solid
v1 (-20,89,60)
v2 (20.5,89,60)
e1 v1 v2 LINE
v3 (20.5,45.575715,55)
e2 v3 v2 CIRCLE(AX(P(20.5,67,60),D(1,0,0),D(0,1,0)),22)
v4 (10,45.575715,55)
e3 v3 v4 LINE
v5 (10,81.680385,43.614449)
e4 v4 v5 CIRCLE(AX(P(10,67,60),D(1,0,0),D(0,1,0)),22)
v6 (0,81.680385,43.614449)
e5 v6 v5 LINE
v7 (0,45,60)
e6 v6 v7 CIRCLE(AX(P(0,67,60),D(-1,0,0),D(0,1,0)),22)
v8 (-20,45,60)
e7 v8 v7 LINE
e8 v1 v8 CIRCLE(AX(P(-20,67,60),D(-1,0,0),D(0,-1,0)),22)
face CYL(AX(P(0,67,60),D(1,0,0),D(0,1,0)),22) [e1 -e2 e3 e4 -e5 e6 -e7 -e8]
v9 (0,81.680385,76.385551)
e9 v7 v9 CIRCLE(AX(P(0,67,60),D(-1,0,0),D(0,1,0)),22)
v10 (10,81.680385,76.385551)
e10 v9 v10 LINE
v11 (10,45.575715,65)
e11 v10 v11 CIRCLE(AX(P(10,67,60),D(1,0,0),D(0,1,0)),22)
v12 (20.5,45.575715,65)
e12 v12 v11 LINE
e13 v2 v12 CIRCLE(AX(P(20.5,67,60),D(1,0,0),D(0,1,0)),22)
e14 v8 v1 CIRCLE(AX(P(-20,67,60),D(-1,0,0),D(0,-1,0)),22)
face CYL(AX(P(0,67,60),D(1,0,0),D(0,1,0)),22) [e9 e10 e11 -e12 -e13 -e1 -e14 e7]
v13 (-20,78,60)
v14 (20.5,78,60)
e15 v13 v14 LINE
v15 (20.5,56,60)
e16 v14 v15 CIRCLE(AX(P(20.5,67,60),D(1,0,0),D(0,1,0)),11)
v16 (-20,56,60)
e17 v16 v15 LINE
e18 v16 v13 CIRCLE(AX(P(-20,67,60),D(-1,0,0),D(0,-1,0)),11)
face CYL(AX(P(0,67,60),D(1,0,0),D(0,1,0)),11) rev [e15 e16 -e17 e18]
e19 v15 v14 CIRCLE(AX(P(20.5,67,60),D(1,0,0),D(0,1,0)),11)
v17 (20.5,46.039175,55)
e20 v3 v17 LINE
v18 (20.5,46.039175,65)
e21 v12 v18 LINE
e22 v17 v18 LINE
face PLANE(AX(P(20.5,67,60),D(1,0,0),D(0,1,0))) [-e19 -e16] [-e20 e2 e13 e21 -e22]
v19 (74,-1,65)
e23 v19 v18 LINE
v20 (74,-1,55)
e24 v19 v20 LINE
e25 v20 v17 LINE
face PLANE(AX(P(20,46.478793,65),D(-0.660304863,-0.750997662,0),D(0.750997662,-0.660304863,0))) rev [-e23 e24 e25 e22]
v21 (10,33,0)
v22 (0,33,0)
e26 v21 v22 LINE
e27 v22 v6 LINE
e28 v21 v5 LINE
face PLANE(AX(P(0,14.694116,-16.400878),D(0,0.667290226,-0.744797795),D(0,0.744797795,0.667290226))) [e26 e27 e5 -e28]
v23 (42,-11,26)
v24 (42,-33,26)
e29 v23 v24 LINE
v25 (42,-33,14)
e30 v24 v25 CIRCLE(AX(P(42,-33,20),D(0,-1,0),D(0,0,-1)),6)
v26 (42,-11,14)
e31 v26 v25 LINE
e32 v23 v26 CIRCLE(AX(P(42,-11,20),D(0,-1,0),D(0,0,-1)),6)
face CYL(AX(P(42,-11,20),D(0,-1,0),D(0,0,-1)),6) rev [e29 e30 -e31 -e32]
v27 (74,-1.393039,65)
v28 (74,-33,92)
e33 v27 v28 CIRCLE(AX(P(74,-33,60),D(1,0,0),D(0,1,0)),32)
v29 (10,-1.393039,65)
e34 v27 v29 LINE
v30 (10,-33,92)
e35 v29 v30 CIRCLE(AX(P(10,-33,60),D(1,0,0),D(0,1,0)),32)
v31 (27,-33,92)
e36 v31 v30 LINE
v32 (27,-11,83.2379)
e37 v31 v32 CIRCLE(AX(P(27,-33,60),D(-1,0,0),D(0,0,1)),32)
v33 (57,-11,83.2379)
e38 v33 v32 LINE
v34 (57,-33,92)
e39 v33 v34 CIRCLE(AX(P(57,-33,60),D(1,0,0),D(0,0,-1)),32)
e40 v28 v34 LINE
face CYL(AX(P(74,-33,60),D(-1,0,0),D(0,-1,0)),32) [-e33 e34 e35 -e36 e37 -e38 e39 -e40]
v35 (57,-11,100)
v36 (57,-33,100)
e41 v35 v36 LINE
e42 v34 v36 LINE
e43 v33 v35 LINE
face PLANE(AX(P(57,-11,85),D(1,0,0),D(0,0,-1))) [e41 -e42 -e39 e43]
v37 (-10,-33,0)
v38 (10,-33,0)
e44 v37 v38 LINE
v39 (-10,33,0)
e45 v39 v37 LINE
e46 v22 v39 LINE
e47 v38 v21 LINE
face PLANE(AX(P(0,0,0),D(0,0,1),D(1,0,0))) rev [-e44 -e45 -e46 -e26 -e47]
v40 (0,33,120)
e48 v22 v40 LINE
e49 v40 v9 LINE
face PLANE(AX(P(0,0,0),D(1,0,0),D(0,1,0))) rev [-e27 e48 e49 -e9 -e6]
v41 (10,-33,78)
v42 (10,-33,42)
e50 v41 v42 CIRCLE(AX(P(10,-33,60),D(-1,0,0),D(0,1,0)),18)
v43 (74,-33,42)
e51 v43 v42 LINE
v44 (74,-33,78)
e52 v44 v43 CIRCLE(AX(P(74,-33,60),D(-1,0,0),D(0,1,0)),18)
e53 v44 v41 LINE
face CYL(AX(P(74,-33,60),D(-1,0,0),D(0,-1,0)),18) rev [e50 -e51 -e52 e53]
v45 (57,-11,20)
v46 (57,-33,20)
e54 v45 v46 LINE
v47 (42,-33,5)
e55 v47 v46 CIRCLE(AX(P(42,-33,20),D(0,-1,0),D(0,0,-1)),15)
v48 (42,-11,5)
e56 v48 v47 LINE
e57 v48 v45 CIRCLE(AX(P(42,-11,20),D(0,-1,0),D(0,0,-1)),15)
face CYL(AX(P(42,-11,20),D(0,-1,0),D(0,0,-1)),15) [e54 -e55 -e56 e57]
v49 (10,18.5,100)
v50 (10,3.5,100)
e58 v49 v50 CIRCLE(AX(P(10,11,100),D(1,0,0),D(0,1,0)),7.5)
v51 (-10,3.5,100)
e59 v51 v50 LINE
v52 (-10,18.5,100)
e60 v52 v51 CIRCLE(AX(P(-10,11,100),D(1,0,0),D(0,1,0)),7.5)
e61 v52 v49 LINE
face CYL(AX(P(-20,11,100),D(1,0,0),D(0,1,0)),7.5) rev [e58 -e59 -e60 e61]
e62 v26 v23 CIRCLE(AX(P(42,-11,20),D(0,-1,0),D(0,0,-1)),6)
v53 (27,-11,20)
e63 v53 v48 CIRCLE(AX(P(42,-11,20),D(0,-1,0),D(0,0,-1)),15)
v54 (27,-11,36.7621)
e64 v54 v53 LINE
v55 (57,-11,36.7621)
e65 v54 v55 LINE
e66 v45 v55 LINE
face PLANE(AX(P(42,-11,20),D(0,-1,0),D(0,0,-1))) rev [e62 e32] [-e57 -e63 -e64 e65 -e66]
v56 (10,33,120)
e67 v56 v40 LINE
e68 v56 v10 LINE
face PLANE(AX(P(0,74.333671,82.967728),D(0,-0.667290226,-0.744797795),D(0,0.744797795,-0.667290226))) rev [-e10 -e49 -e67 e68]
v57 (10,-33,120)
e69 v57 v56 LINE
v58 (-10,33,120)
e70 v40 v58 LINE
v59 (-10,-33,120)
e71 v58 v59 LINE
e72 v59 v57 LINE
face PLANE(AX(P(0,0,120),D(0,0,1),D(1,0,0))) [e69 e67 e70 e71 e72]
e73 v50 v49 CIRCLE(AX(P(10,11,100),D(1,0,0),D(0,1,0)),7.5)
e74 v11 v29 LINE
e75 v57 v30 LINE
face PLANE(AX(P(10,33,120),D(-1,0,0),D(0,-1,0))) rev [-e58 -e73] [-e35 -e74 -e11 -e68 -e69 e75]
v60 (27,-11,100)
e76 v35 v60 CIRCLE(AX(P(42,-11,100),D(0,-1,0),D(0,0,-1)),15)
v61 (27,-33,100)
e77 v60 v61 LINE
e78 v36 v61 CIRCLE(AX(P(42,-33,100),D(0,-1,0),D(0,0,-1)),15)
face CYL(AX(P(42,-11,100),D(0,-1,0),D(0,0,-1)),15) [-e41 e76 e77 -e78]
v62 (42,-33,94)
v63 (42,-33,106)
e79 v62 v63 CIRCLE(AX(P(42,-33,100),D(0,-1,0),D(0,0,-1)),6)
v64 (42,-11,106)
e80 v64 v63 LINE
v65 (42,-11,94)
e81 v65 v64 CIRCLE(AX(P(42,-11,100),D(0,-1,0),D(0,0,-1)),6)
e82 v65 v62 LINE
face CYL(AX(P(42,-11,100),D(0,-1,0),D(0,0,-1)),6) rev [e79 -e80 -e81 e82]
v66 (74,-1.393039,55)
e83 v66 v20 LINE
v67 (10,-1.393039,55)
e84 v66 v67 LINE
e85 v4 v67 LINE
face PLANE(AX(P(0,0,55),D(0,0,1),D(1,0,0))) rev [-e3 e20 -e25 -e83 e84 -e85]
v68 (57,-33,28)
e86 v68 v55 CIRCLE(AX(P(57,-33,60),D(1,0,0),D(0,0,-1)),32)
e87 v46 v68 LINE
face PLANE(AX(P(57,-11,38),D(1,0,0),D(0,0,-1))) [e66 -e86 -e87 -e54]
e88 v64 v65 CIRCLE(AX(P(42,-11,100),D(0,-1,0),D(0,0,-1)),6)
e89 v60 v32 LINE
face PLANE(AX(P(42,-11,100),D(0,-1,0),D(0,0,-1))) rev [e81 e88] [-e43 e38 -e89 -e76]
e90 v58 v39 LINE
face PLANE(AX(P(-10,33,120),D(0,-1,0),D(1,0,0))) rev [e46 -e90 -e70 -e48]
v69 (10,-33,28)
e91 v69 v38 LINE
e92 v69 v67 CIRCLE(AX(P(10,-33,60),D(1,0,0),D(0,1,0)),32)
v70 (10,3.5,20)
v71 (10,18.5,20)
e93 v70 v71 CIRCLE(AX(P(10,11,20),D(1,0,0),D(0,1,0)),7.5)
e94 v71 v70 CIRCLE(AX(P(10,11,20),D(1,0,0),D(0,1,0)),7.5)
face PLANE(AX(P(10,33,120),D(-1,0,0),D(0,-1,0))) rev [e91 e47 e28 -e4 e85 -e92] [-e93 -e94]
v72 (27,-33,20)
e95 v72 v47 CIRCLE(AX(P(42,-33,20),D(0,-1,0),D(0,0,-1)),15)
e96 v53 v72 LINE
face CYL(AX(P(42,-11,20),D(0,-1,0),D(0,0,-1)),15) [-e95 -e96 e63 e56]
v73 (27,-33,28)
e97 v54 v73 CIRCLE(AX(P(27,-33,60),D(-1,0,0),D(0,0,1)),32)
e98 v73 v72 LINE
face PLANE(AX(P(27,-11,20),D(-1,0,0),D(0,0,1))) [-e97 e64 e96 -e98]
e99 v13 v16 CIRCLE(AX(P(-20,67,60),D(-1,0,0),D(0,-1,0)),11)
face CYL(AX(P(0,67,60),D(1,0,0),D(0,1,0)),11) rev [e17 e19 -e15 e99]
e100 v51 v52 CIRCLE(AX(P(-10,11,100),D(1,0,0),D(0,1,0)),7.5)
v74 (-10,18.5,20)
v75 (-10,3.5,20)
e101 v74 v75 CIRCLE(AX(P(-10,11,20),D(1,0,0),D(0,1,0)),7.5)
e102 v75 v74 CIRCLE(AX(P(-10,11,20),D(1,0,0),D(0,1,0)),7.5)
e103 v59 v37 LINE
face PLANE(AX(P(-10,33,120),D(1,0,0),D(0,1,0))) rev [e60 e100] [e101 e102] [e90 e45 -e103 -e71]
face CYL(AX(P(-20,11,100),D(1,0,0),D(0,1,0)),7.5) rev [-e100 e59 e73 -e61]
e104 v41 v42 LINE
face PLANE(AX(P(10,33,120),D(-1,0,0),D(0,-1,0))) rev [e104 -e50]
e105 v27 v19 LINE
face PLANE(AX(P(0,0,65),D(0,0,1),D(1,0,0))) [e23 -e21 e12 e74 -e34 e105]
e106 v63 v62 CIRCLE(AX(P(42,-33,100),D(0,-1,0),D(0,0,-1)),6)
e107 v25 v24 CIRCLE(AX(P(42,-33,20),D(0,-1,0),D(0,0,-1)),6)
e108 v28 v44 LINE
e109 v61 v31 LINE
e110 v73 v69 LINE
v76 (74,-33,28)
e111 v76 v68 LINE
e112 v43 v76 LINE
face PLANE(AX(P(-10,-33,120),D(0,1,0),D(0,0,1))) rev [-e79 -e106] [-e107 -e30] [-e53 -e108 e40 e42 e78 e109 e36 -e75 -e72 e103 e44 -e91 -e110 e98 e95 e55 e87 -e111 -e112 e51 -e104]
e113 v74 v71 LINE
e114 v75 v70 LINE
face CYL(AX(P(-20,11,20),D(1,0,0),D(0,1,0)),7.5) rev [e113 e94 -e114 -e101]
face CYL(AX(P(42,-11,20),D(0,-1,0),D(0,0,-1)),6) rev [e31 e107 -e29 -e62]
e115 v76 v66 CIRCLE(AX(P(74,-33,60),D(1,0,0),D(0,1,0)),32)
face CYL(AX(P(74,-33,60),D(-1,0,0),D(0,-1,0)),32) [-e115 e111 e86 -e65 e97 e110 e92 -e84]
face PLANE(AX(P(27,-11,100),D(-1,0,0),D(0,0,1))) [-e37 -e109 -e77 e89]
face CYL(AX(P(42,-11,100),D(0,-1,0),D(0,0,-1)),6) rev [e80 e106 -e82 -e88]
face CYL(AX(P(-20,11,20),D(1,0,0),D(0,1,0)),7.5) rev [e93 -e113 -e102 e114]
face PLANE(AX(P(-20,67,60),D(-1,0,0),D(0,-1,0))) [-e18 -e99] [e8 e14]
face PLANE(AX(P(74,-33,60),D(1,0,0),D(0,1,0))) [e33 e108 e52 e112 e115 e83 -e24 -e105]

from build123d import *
from build123d.topology import SkipClean

# Parameters (mm, degrees)
BASE_PLATE_SKETCH_W            = 20
BASE_PLATE_SKETCH_H            = 66
BASE_PLATE_DEPTH               = 120
UPRIGHT_WEB_SKETCH_R           = 22
UPRIGHT_WEB_SKETCH_R_2         = 11
UPRIGHT_WEB_DEPTH              = 10
TRUNNION_BOSS_FRONT_SKETCH_R   = 22
TRUNNION_BOSS_FRONT_SKETCH_R_2 = 11
TRUNNION_BOSS_FRONT_DEPTH      = 20
TRUNNION_START                 = 10
TRUNNION_BOSS_REAR_SKETCH_R    = 22
TRUNNION_BOSS_REAR_SKETCH_R_2  = 11
TRUNNION_BOSS_REAR_DEPTH       = 10
BRACKET_HOLES_SKETCH_R         = 7.5
BRACKET_HOLES_DEPTH            = 30
SEMI_CIRCULAR_BASE_DEPTH       = 64
GUSSET_1_DEPTH                 = 5
GUSSET_START                   = -64
GUSSET_2_DEPTH                 = 64
TRUNNION_START_2               = 0.5
TRUNNION_FACE_PAD_SKETCH_R     = 22
TRUNNION_FACE_PAD_SKETCH_R_2   = 11
TRUNNION_FACE_PAD_0_5MM_DEPTH  = 0.5
BASE_MOUNTING_LUGS_SKETCH_R    = 6
BASE_MOUNTING_LUGS_DEPTH       = 22


with BuildPart() as part:
    # Base Plate Sketch → Base Plate (new body)
    with BuildSketch(Plane.XY):
        Rectangle(BASE_PLATE_SKETCH_W, BASE_PLATE_SKETCH_H)
    extrude(amount=BASE_PLATE_DEPTH)

    # Upright Web Sketch → Upright Web (add)
    # profile 1 of 2: a face of its own
    with BuildSketch(Plane(origin=(10, 0, 0), x_dir=(0, 0, -1), z_dir=(1, 0, 0))):
        with BuildLine():
            Line((-76.38555148, 81.680384964), (-120, 33))
            Line((-120, 33), (0, 33))
            Line((0, 33), (-43.61444852, 81.680384964))
            ThreePointArc((-43.61444852, 81.680384964), (-39.451494792, 74.858685241), (-38, 67))
            ThreePointArc((-38, 67), (-67.858685241, 46.451494792), (-76.38555148, 81.680384964))
        make_face()
    # profile 2 of 2: a face of its own
    with BuildSketch(Plane(origin=(10, 0, 0), x_dir=(0, 0, -1), z_dir=(1, 0, 0))):
        with Locations((-60, 67)):
            Circle(UPRIGHT_WEB_SKETCH_R)
        with Locations(Location((-60, 67, 0), (0, 0, 90))):
            Circle(UPRIGHT_WEB_SKETCH_R_2, mode=Mode.SUBTRACT)
    extrude(amount=-UPRIGHT_WEB_DEPTH)

    # Trunnion Boss Front Sketch → Trunnion Boss Front (add)
    with SkipClean():  # the faces are left unmerged after this step: merging them gives an invalid solid
        with BuildSketch(Plane.ZY):
            with Locations(Location((60, 67, 0), (0, 0, 41.858266049))):
                Circle(TRUNNION_BOSS_FRONT_SKETCH_R)
            with Locations(Location((60, 67, 0), (0, 0, 90))):
                Circle(TRUNNION_BOSS_FRONT_SKETCH_R_2, mode=Mode.SUBTRACT)
        extrude(amount=TRUNNION_BOSS_FRONT_DEPTH)

    # Trunnion Boss Rear Sketch → Trunnion Boss Rear (add)
    with SkipClean():  # the faces are left unmerged after this step: merging them gives an invalid solid
        with BuildSketch(Plane(origin=(10, 0, 0), x_dir=(0, 0, -1), z_dir=(1, 0, 0)).offset(TRUNNION_START)):
            with Locations(Location((-60, 67, 0), (0, 0, 90))):
                Circle(TRUNNION_BOSS_REAR_SKETCH_R)
            with Locations(Location((-60, 67, 0), (0, 0, 90))):
                Circle(TRUNNION_BOSS_REAR_SKETCH_R_2, mode=Mode.SUBTRACT)
        extrude(amount=-TRUNNION_BOSS_REAR_DEPTH)

    # Bracket Holes Sketch → Bracket Holes (cut)
    with SkipClean():  # the faces are left unmerged after this step: merging them gives an invalid solid
        with BuildSketch(Plane(origin=(10, 0, 0), x_dir=(0, 0, -1), z_dir=(1, 0, 0))):
            with Locations(Location((-100, 11, 0), (0, 0, 90))):
                Circle(BRACKET_HOLES_SKETCH_R)
            with Locations(Location((-20, 11, 0), (0, 0, 90))):
                Circle(BRACKET_HOLES_SKETCH_R)
        extrude(amount=-BRACKET_HOLES_DEPTH, mode=Mode.SUBTRACT)

    # Semi-Circular Base Sketch → Semi-Circular Base (add)
    with SkipClean():  # the faces are left unmerged after this step: merging them gives an invalid solid
        with BuildSketch(Plane(origin=(10, 0, 0), x_dir=(0, 0, -1), z_dir=(1, 0, 0))):
            with BuildLine():
                Line((-92, -33), (-78, -33))
                ThreePointArc((-78, -33), (-60, -15), (-42, -33))
                Line((-42, -33), (-28, -33))
                ThreePointArc((-28, -33), (-60, -1), (-92, -33))
            make_face()
        extrude(amount=SEMI_CIRCULAR_BASE_DEPTH)



with BuildPart() as body_2:
    # Gusset 1 Sketch → Gusset 1 (new, symmetric)
    with BuildSketch(Plane.XY.offset(60)):
        Polygon((10, -5), (10, 46.478793063), (20, 46.478793063), (74, -1), (74, -5), align=None)
    extrude(amount=GUSSET_1_DEPTH, both=True)


with BuildPart() as part_1:
    with SkipClean():  # the faces are left unmerged after this step: merging them gives an invalid solid
        add(part.part)

        add(body_2.part)  # Gusset 2 merges body 2
        # Gusset 2 Sketch → Gusset 2 (add)
        with BuildSketch(Plane(origin=(74, 0, 0), x_dir=(0, 0, -1), z_dir=(1, 0, 0)).offset(GUSSET_START)):
            with BuildLine():
                Line((-92, -33), (-78, -33))
                ThreePointArc((-78, -33), (-60, -15), (-42, -33))
                Line((-42, -33), (-28, -33))
                ThreePointArc((-28, -33), (-60, -1), (-92, -33))
            make_face()
        extrude(amount=GUSSET_2_DEPTH)

    # Trunnion Face Pad Sketch → Trunnion Face Pad 0.5mm (add)
    with SkipClean():  # the faces are left unmerged after this step: merging them gives an invalid solid
        with BuildSketch(Plane(origin=(20, 0, 0), x_dir=(0, 0, -1), z_dir=(1, 0, 0)).offset(TRUNNION_START_2)):
            with Locations(Location((-60, 67, 0), (0, 0, 138.141733951))):
                Circle(TRUNNION_FACE_PAD_SKETCH_R)
            with Locations(Location((-60, 67, 0), (0, 0, 90))):
                Circle(TRUNNION_FACE_PAD_SKETCH_R_2, mode=Mode.SUBTRACT)
        extrude(amount=-TRUNNION_FACE_PAD_0_5MM_DEPTH)

    # Base Mounting Lugs Sketch → Base Mounting Lugs (add)
    # profile 1 of 2: a face of its own
    with SkipClean():  # the faces are left unmerged after this step: merging them gives an invalid solid
        with BuildSketch(Plane.XZ.offset(33)):
            with BuildLine():
                Line((27, 100), (27, 83))
                Line((27, 83), (57, 83))
                Line((57, 83), (57, 85))
                Line((57, 85), (57, 100))
                ThreePointArc((57, 100), (42, 115), (27, 100))
            make_face()
            with Locations(Location((42, 100, 0), (0, 0, 270))):
                Circle(BASE_MOUNTING_LUGS_SKETCH_R, mode=Mode.SUBTRACT)
        # profile 2 of 2: a face of its own
        with BuildSketch(Plane.XZ.offset(33)):
            with BuildLine():
                Line((27, 20), (27, 38))
                Line((27, 38), (57, 38))
                Line((57, 38), (57, 35))
                Line((57, 35), (57, 20))
                ThreePointArc((57, 20), (42, 5), (27, 20))
            make_face()
            with Locations(Location((42, 20, 0), (0, 0, 270))):
                Circle(BASE_MOUNTING_LUGS_SKETCH_R, mode=Mode.SUBTRACT)
        extrude(amount=-BASE_MOUNTING_LUGS_DEPTH)


solid = part_1.part
